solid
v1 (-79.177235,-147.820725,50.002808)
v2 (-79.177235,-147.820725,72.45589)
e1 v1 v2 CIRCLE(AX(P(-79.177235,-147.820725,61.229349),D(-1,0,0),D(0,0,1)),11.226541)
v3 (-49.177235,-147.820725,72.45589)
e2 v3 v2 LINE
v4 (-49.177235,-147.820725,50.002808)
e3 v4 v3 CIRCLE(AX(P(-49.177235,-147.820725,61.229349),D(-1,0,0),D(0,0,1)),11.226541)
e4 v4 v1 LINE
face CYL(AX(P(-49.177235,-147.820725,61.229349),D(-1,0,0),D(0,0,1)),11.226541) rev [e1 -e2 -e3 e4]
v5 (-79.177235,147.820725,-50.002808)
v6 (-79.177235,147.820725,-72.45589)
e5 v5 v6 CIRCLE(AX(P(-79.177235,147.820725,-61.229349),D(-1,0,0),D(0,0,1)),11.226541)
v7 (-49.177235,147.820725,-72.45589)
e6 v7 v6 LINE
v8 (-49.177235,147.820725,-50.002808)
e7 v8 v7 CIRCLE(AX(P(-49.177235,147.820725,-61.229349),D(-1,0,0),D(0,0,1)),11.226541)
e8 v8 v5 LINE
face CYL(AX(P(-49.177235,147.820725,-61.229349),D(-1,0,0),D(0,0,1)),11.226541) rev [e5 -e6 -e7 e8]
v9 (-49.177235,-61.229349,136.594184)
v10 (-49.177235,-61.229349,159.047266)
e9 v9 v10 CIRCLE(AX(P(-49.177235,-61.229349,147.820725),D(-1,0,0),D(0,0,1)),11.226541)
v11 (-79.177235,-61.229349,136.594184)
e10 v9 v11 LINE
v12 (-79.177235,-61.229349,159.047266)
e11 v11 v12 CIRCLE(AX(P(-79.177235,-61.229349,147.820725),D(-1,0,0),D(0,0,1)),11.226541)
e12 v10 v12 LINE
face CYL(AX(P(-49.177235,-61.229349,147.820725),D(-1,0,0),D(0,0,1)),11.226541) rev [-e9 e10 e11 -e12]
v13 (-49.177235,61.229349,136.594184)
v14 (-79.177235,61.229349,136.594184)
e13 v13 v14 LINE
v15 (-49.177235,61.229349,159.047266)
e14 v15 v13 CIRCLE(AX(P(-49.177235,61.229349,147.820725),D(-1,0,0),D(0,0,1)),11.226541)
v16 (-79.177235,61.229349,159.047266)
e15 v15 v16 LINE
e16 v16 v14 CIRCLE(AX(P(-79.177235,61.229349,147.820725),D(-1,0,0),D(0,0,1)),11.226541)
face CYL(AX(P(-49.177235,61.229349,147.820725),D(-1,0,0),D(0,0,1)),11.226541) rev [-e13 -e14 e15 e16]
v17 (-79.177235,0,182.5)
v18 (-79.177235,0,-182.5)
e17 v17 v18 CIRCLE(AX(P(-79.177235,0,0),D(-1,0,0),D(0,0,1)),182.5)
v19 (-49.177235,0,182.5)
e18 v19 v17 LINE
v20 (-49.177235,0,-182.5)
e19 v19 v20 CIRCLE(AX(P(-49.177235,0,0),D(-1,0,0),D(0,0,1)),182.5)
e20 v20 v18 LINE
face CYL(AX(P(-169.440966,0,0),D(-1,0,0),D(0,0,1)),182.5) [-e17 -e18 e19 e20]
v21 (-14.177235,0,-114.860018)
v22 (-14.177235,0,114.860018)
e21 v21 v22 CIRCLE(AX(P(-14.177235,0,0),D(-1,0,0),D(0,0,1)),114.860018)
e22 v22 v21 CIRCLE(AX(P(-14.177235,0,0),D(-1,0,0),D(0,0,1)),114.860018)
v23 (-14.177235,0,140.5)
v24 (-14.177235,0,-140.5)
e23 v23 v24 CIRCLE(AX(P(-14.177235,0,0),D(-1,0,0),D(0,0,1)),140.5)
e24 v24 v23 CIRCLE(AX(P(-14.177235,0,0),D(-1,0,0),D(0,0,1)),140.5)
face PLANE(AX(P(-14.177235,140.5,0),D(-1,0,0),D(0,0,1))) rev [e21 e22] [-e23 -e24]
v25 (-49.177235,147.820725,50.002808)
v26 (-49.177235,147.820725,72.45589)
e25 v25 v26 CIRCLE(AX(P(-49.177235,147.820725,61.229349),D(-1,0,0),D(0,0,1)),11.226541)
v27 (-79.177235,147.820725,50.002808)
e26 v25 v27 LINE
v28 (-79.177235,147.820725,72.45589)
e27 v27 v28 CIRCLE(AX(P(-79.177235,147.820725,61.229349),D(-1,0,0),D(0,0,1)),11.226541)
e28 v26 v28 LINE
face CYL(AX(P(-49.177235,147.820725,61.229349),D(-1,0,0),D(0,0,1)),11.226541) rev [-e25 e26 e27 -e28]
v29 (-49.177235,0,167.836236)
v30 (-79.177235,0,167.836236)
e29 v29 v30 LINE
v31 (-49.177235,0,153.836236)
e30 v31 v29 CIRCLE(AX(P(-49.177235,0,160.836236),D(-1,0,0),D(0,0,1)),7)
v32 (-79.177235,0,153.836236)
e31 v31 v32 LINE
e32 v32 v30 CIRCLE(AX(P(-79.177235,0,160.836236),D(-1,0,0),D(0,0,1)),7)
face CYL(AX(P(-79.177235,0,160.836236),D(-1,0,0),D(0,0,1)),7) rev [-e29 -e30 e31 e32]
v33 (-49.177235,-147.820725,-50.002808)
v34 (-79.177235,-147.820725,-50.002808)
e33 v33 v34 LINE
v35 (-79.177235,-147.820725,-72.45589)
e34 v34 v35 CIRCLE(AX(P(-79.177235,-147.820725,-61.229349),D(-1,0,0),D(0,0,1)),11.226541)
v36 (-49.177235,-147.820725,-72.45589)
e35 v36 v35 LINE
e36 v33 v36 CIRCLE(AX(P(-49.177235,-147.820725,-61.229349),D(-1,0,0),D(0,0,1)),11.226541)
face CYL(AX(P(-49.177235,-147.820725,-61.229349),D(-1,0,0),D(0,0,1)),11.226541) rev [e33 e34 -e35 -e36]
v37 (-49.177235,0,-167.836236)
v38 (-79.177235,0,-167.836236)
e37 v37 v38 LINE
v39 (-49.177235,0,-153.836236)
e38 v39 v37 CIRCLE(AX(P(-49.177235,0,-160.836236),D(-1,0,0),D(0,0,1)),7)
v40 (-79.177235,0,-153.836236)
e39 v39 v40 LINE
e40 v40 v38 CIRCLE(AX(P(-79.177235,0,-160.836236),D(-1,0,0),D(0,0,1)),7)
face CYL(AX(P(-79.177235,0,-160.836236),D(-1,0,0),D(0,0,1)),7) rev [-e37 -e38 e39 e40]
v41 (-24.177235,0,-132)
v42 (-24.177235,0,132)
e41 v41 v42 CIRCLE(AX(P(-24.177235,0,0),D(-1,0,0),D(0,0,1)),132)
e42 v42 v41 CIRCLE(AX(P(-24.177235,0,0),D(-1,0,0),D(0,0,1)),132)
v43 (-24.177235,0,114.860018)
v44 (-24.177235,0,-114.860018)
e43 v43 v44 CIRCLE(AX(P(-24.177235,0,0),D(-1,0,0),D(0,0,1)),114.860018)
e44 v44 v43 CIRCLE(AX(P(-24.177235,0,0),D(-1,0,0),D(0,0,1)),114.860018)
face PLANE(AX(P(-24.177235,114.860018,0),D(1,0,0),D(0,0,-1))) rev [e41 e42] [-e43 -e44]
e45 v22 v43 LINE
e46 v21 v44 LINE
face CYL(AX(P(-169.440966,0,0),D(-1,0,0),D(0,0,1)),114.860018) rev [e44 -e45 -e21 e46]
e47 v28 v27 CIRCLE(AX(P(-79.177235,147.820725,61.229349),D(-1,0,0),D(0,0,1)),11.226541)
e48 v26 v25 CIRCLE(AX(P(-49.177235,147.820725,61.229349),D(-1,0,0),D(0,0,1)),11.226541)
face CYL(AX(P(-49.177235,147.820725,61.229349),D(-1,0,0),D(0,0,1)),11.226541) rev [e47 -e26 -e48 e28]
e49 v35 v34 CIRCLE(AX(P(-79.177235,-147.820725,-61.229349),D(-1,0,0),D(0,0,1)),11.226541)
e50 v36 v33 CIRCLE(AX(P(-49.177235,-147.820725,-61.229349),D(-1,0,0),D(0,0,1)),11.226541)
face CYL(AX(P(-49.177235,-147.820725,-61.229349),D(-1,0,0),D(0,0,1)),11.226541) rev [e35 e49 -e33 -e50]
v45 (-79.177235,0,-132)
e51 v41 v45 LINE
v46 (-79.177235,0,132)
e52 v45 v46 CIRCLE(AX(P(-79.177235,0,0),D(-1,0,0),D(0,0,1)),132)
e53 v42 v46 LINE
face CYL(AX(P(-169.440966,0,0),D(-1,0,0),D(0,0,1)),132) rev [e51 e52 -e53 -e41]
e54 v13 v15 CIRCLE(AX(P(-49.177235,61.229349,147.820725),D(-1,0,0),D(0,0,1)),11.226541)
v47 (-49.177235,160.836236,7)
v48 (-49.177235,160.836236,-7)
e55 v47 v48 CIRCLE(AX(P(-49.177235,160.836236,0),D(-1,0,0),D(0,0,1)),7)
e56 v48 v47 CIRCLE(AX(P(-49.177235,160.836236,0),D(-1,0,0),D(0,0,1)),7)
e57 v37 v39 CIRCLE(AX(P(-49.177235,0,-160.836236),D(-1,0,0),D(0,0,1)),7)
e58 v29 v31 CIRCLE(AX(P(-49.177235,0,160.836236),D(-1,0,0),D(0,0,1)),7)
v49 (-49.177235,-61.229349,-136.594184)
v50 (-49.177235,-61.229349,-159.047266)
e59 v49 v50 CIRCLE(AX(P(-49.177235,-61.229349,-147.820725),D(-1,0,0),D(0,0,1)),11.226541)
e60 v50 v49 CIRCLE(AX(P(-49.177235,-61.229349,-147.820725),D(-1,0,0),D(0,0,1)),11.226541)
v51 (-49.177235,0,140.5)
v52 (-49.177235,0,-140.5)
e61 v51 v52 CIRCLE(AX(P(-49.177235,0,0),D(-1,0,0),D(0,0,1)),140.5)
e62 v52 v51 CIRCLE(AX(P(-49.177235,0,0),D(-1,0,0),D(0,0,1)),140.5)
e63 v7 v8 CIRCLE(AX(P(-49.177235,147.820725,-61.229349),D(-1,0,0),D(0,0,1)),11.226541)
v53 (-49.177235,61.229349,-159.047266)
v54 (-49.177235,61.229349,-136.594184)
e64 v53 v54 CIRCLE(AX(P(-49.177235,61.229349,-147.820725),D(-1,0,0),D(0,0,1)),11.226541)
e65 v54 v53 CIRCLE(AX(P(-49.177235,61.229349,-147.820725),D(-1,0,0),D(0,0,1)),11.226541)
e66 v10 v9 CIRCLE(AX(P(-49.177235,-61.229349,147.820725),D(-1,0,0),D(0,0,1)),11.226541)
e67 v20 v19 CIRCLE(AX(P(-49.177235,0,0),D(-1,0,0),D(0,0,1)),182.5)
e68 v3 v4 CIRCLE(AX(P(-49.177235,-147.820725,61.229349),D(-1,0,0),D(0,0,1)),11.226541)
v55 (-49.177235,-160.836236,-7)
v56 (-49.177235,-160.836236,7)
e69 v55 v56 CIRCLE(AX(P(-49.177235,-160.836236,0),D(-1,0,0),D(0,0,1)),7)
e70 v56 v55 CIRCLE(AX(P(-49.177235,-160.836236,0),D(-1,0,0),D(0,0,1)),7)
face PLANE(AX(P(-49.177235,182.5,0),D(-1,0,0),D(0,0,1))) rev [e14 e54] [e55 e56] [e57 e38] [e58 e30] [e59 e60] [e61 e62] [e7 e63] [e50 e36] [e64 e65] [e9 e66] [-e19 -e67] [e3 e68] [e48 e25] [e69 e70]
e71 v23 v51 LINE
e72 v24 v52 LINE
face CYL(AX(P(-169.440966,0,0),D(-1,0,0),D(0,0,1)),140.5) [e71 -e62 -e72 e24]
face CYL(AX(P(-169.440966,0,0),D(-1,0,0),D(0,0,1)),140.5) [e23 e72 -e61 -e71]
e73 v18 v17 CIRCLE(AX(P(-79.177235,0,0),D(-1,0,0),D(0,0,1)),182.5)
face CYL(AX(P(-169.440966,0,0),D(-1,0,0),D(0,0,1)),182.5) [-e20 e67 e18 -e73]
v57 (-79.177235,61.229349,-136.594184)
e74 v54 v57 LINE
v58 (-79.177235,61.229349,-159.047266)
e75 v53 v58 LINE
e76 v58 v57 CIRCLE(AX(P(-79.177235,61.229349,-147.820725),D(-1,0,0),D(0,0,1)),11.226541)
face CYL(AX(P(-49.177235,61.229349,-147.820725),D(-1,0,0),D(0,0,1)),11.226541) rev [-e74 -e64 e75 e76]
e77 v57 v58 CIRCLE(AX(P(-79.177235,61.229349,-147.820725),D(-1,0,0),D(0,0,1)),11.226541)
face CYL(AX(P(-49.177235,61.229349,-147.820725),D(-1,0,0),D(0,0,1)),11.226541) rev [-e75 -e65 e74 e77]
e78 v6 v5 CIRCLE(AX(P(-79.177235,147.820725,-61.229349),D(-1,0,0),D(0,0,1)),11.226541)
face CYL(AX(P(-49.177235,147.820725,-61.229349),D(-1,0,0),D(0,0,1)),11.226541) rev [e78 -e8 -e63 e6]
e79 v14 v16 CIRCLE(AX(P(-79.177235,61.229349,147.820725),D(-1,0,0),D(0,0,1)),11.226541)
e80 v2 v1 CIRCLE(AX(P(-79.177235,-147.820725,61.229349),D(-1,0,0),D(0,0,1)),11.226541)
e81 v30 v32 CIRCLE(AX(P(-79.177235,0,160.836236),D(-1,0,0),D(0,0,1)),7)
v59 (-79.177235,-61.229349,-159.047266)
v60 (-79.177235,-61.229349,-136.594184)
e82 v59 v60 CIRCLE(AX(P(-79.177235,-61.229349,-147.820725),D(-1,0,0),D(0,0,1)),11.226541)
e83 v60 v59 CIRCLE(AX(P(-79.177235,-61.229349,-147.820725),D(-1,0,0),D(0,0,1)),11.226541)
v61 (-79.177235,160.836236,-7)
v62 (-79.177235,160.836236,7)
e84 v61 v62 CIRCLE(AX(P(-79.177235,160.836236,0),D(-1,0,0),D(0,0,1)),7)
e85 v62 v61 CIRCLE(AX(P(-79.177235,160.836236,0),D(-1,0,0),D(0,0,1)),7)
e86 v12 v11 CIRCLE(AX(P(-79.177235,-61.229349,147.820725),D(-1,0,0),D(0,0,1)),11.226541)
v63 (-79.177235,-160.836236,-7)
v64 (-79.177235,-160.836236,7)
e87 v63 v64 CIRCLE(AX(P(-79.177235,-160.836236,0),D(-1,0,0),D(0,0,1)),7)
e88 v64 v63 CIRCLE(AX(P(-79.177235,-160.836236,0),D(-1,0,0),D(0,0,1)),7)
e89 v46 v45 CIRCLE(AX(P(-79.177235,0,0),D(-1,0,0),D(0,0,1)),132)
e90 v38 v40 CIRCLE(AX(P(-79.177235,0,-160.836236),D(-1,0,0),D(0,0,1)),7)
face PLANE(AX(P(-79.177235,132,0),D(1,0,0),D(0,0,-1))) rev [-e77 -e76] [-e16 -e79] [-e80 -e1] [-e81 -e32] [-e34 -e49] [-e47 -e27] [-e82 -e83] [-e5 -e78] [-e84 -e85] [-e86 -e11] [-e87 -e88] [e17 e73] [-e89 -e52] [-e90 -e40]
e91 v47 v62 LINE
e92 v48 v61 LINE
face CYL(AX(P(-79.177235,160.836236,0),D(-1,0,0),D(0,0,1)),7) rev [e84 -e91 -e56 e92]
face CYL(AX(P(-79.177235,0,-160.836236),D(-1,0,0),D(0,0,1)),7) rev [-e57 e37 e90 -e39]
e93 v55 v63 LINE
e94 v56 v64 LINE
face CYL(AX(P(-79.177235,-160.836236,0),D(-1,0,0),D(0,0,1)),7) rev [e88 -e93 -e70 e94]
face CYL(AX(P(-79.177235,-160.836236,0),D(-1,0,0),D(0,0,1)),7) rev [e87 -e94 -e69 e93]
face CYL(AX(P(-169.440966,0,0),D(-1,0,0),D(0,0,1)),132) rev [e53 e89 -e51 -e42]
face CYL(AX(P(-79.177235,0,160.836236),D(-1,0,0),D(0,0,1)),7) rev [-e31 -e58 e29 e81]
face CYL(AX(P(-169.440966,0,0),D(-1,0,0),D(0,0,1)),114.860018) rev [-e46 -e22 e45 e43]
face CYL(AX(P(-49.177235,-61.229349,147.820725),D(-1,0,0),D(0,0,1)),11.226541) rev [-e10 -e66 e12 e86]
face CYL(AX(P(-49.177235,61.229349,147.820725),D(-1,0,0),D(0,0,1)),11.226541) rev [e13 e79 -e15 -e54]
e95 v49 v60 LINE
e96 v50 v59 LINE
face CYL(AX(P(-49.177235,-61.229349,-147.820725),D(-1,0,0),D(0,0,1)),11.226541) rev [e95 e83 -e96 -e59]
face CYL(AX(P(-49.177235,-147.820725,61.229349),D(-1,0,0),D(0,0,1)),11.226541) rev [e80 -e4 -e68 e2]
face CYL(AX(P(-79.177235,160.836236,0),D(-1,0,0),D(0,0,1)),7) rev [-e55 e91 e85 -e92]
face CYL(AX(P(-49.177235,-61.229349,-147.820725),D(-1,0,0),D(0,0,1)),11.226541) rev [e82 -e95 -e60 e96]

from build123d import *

# Parameters (mm, degrees)
SKETCH2_R          = 11.22654111
CUT_EXTRUDE1_DEPTH = 30
CIRPATTERN1_COUNT  = 4


with BuildPart() as part:
    # Sketch1 → Revolve1 (revolve)
    with BuildSketch(Plane.XY, mode=Mode.PRIVATE) as revolve1_sk:
        Polygon((-79.177234861, 132), (-79.177234861, 182.5), (-49.177234861, 182.5), (-49.177234861, 140.5), (-14.177234861, 140.5), (-14.177234861, 114.860017889), (-24.177234861, 114.860017889), (-24.177234861, 132), align=None)
    revolve(revolve1_sk.sketch.rotate(Axis((-169.440966011, 0, 0), (1, 0, 0)), 90), axis=Axis((-169.440966011, 0, 0), (1, 0, 0)))

    # Sketch2 → Cut-Extrude1 (cut)
    with BuildSketch(Plane.ZY.offset(79.177234861)):
        with Locations((61.229349178, 147.820725202)):
            Circle(SKETCH2_R)
        with Locations((147.820725202, 61.229349178)):
            Circle(SKETCH2_R)
        with Locations((147.820725202, -61.229349178)):
            Circle(SKETCH2_R)
        with Locations((61.229349178, -147.820725202)):
            Circle(SKETCH2_R)
        with Locations((-61.229349178, -147.820725202)):
            Circle(SKETCH2_R)
        with Locations((-147.820725202, -61.229349178)):
            Circle(SKETCH2_R)
        with Locations((-147.820725202, 61.229349178)):
            Circle(SKETCH2_R)
        with Locations((-61.229349178, 147.820725202)):
            Circle(SKETCH2_R)
    extrude(amount=-CUT_EXTRUDE1_DEPTH, mode=Mode.SUBTRACT)

    # Sketch6 → M16 Tapped Hole1 (revolve, cut)
    with BuildSketch(Plane(origin=(-79.177234861, 160.836236417, 0), x_dir=(0, 0, 1), z_dir=(0, 1, 0))):
        Polygon((0, 0), (0, 46.206024333), (7, 42), (7, 0), align=None)
    m16_tapped_hole1 = revolve(axis=Axis((-85.527234861, 160.836236417, 0), (1, 0, 0)), mode=Mode.SUBTRACT)

    # CirPattern1: M16 Tapped Hole1 ×4 about axis
    cirpattern1_axis = Axis((0, 0, 0), (1, 0, 0))
    for i in range(1, CIRPATTERN1_COUNT):
        add(m16_tapped_hole1.rotate(cirpattern1_axis, i * 360 / CIRPATTERN1_COUNT), mode=Mode.SUBTRACT)


solid = part.part
